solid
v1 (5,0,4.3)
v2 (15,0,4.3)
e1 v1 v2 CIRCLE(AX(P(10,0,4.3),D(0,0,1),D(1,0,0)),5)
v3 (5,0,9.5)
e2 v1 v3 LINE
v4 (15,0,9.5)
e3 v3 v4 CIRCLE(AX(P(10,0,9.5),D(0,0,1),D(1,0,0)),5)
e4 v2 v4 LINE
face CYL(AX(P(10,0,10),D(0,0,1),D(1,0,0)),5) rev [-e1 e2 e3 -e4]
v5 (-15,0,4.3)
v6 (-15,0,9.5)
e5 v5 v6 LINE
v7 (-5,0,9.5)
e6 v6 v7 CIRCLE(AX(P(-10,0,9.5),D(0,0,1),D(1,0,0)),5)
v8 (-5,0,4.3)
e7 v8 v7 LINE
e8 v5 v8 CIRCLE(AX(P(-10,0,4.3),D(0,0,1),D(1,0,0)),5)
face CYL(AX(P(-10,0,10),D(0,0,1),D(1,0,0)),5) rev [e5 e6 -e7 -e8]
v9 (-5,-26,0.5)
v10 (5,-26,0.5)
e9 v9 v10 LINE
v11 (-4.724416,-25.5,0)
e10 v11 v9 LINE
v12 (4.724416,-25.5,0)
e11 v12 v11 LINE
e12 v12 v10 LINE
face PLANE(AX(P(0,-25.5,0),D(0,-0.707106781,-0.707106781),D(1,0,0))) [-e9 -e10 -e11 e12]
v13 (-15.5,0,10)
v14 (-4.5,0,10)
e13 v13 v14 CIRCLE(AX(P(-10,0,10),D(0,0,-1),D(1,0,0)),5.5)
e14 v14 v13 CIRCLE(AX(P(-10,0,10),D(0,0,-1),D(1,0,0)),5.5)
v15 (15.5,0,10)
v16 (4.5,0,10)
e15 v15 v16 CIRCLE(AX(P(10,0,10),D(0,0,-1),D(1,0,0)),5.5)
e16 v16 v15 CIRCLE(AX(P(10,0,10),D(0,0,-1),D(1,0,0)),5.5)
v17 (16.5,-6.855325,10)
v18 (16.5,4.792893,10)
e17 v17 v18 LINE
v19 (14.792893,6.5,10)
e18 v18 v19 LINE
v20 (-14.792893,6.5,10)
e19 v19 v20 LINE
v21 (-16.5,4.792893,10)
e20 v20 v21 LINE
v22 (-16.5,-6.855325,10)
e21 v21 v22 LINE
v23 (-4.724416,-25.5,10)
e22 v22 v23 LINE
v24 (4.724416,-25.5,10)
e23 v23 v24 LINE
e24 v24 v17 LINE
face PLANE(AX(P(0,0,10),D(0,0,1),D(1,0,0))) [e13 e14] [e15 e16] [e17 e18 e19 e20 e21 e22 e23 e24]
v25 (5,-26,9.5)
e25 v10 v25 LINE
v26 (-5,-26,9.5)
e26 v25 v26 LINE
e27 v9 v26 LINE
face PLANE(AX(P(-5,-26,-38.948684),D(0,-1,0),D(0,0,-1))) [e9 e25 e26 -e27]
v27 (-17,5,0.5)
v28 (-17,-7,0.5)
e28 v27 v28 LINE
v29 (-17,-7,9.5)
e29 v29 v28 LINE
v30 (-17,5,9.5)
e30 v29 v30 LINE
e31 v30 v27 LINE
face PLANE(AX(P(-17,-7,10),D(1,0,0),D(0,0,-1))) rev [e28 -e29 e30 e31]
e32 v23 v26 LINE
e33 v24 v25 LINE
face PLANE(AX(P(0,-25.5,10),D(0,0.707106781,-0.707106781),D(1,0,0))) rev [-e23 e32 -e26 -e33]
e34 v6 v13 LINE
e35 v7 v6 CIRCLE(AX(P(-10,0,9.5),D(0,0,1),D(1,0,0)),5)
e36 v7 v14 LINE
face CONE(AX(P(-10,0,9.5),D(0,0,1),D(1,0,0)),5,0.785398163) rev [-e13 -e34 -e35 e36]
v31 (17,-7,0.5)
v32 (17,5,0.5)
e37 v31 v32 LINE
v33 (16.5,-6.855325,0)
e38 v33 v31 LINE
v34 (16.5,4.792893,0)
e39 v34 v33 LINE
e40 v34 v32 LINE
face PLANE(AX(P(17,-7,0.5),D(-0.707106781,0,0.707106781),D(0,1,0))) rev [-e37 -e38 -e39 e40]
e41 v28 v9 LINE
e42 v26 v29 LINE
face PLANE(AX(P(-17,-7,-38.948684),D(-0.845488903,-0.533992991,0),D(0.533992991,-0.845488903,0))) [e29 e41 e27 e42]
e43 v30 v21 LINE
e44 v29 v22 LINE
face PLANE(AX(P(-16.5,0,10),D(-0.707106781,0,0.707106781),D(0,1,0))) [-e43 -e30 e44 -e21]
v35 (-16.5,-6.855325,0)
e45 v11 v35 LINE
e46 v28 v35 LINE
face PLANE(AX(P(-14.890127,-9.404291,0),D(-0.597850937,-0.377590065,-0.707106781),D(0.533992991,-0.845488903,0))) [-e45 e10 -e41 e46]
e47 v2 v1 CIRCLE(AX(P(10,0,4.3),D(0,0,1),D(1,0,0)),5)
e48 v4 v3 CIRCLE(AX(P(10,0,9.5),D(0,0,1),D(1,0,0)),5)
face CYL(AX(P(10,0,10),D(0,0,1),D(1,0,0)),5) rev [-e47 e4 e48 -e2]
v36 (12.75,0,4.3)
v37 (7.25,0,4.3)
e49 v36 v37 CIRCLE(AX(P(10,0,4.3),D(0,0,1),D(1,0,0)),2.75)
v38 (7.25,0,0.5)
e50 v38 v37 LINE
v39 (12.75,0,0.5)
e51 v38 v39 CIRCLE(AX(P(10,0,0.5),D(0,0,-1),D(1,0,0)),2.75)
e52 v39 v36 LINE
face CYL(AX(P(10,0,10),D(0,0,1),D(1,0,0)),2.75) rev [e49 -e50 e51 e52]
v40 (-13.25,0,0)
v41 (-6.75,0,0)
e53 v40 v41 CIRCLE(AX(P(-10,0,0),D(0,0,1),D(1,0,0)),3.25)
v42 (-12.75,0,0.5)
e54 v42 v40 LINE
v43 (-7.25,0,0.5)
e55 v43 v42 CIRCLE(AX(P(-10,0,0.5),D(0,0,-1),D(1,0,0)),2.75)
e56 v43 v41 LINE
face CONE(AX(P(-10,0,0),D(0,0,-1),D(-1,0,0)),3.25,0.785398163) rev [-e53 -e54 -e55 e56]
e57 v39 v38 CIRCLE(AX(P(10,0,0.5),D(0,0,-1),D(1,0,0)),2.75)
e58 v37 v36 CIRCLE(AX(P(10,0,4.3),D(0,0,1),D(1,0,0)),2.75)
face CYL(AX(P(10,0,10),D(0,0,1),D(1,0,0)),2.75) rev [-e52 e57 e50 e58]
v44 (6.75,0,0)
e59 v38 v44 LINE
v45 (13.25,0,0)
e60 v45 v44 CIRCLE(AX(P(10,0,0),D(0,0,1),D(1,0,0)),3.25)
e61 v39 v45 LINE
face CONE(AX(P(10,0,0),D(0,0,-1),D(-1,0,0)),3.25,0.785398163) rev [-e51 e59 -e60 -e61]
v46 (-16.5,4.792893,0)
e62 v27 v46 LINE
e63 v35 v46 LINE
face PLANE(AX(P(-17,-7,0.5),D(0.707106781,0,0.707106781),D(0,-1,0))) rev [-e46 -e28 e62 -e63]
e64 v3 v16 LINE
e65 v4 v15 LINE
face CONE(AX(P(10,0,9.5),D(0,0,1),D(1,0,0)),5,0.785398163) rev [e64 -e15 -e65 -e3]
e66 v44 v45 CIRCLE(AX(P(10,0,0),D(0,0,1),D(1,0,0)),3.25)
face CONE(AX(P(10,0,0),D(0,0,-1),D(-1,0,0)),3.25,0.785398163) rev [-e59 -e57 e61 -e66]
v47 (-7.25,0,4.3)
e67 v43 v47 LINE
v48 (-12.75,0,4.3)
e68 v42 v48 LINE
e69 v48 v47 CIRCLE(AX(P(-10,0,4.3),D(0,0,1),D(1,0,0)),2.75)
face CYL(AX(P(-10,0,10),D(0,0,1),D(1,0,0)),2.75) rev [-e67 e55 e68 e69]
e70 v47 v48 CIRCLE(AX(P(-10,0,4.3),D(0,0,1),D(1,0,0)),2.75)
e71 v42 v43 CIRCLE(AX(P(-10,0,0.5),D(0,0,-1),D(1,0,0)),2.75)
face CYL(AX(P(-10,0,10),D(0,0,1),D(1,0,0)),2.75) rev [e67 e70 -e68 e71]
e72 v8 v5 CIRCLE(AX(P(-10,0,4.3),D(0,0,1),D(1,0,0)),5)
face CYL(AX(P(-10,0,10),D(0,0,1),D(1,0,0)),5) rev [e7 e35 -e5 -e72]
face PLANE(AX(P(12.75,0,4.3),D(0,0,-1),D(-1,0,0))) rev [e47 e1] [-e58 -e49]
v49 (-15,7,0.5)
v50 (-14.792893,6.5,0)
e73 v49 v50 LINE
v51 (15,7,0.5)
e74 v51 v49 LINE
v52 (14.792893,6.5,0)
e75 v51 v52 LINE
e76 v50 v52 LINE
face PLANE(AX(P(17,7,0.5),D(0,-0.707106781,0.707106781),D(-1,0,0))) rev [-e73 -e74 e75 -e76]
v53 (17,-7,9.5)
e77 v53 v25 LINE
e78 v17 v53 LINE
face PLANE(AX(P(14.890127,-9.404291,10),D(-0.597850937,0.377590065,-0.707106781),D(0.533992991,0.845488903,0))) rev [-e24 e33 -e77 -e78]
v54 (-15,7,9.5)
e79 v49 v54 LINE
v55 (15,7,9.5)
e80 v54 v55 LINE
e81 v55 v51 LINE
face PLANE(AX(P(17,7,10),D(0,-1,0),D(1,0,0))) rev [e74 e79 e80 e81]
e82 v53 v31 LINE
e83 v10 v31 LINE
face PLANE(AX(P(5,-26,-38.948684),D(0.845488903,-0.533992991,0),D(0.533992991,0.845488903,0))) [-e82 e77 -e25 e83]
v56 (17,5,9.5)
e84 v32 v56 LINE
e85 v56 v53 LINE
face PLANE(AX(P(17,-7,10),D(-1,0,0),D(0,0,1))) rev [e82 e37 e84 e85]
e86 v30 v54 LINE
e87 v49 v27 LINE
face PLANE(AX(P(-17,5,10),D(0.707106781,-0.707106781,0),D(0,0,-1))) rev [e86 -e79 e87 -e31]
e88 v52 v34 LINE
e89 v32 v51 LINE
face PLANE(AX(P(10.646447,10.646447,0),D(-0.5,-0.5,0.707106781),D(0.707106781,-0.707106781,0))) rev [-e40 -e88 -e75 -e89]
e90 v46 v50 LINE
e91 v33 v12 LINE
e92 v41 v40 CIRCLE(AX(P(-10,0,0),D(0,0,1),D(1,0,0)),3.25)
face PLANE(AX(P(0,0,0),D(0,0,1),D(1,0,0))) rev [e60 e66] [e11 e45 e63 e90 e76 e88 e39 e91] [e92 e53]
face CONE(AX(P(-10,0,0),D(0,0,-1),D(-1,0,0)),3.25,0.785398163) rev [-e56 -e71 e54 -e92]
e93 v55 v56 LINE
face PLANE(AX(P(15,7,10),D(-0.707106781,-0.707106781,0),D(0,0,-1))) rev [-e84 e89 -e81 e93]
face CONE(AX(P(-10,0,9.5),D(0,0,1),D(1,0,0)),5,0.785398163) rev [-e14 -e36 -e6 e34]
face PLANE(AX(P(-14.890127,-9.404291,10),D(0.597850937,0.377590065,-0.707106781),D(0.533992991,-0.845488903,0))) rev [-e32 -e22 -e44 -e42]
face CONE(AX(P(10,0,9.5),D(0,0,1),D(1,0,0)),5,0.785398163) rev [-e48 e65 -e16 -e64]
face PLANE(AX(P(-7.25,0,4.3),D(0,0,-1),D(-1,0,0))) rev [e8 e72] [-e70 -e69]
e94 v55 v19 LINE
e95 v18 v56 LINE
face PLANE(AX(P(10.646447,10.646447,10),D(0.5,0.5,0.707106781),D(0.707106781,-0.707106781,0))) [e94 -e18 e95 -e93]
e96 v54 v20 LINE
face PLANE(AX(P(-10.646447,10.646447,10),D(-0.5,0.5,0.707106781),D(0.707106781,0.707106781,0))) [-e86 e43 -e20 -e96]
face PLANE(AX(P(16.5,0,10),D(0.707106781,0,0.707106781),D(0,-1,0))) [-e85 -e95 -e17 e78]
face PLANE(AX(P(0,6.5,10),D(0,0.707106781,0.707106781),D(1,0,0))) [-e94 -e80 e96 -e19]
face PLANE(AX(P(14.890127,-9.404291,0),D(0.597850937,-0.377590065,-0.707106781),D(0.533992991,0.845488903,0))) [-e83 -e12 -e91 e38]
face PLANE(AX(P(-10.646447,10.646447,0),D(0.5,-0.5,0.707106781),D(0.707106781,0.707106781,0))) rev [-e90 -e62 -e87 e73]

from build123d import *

# Parameters (mm, degrees)
SKETCH1_W                                            = 34
SKETCH1_H                                            = 14
BOSS_EXTRUDE1_DEPTH                                  = 10
HOLE_SIZE_PER_SOCKET_HEAD_CAP_SCREW_TYPE_D           = 5.5
HOLE_SIZE_PER_SOCKET_HEAD_CAP_SCREW_TYPE_CBORE_D     = 10
HOLE_SIZE_PER_SOCKET_HEAD_CAP_SCREW_TYPE_CBORE_DEPTH = 5.7
BOSS_EXTRUDE2_DEPTH                                  = 10
CHAMFER2_SIZE                                        = 2
CHAMFER1_SIZE                                        = 0.5


with BuildPart() as part:
    # Sketch1 → Boss-Extrude1 (new body)
    with BuildSketch(Plane.XY):
        Rectangle(SKETCH1_W, SKETCH1_H)
    extrude(amount=BOSS_EXTRUDE1_DEPTH)

    # Hole size per socket head cap screw type1 (through all)
    with Locations(Plane(origin=(-10, 0, 10), x_dir=(1, 0, 0), z_dir=(0, 0, 1))):
        with Locations((0, 0), (20, 0)):
            CounterBoreHole(HOLE_SIZE_PER_SOCKET_HEAD_CAP_SCREW_TYPE_D / 2, HOLE_SIZE_PER_SOCKET_HEAD_CAP_SCREW_TYPE_CBORE_D / 2, HOLE_SIZE_PER_SOCKET_HEAD_CAP_SCREW_TYPE_CBORE_DEPTH)

    # Sketch3 → Boss-Extrude2 (add)
    with BuildSketch(Plane.XY.offset(10)):
        Polygon((-17, -7), (-5, -26), (5, -26), (17, -7), align=None)
    extrude(amount=-BOSS_EXTRUDE2_DEPTH)

    # Chamfer2
    chamfer2_edges = [part.edges().sort_by_distance(p)[0] for p in [
        (-17, 7, 5),
        (17, 7, 5),
    ]]
    chamfer(chamfer2_edges, length=CHAMFER2_SIZE)

    # Chamfer1
    chamfer1_edges = [part.edges().sort_by_distance(p)[0] for p in [
        (17, -1, 10),
        (5, 0, 10),
        (12.75, 0, 0),
        (-15, 0, 10),
        (-7.25, 0, 0),
        (-11, -16.5, 10),
        (0, -26, 10),
        (11, -16.5, 10),
        (11, -16.5, 0),
        (0, -26, 0),
        (-11, -16.5, 0),
        (-17, -1, 0),
        (-17, -1, 10),
        (0, 7, 0),
        (16, 6, 0),
        (-16, 6, 0),
        (0, 7, 10),
        (16, 6, 10),
        (-16, 6, 10),
        (17, -1, 0),
    ]]
    chamfer(chamfer1_edges, length=CHAMFER1_SIZE)


solid = part.part
